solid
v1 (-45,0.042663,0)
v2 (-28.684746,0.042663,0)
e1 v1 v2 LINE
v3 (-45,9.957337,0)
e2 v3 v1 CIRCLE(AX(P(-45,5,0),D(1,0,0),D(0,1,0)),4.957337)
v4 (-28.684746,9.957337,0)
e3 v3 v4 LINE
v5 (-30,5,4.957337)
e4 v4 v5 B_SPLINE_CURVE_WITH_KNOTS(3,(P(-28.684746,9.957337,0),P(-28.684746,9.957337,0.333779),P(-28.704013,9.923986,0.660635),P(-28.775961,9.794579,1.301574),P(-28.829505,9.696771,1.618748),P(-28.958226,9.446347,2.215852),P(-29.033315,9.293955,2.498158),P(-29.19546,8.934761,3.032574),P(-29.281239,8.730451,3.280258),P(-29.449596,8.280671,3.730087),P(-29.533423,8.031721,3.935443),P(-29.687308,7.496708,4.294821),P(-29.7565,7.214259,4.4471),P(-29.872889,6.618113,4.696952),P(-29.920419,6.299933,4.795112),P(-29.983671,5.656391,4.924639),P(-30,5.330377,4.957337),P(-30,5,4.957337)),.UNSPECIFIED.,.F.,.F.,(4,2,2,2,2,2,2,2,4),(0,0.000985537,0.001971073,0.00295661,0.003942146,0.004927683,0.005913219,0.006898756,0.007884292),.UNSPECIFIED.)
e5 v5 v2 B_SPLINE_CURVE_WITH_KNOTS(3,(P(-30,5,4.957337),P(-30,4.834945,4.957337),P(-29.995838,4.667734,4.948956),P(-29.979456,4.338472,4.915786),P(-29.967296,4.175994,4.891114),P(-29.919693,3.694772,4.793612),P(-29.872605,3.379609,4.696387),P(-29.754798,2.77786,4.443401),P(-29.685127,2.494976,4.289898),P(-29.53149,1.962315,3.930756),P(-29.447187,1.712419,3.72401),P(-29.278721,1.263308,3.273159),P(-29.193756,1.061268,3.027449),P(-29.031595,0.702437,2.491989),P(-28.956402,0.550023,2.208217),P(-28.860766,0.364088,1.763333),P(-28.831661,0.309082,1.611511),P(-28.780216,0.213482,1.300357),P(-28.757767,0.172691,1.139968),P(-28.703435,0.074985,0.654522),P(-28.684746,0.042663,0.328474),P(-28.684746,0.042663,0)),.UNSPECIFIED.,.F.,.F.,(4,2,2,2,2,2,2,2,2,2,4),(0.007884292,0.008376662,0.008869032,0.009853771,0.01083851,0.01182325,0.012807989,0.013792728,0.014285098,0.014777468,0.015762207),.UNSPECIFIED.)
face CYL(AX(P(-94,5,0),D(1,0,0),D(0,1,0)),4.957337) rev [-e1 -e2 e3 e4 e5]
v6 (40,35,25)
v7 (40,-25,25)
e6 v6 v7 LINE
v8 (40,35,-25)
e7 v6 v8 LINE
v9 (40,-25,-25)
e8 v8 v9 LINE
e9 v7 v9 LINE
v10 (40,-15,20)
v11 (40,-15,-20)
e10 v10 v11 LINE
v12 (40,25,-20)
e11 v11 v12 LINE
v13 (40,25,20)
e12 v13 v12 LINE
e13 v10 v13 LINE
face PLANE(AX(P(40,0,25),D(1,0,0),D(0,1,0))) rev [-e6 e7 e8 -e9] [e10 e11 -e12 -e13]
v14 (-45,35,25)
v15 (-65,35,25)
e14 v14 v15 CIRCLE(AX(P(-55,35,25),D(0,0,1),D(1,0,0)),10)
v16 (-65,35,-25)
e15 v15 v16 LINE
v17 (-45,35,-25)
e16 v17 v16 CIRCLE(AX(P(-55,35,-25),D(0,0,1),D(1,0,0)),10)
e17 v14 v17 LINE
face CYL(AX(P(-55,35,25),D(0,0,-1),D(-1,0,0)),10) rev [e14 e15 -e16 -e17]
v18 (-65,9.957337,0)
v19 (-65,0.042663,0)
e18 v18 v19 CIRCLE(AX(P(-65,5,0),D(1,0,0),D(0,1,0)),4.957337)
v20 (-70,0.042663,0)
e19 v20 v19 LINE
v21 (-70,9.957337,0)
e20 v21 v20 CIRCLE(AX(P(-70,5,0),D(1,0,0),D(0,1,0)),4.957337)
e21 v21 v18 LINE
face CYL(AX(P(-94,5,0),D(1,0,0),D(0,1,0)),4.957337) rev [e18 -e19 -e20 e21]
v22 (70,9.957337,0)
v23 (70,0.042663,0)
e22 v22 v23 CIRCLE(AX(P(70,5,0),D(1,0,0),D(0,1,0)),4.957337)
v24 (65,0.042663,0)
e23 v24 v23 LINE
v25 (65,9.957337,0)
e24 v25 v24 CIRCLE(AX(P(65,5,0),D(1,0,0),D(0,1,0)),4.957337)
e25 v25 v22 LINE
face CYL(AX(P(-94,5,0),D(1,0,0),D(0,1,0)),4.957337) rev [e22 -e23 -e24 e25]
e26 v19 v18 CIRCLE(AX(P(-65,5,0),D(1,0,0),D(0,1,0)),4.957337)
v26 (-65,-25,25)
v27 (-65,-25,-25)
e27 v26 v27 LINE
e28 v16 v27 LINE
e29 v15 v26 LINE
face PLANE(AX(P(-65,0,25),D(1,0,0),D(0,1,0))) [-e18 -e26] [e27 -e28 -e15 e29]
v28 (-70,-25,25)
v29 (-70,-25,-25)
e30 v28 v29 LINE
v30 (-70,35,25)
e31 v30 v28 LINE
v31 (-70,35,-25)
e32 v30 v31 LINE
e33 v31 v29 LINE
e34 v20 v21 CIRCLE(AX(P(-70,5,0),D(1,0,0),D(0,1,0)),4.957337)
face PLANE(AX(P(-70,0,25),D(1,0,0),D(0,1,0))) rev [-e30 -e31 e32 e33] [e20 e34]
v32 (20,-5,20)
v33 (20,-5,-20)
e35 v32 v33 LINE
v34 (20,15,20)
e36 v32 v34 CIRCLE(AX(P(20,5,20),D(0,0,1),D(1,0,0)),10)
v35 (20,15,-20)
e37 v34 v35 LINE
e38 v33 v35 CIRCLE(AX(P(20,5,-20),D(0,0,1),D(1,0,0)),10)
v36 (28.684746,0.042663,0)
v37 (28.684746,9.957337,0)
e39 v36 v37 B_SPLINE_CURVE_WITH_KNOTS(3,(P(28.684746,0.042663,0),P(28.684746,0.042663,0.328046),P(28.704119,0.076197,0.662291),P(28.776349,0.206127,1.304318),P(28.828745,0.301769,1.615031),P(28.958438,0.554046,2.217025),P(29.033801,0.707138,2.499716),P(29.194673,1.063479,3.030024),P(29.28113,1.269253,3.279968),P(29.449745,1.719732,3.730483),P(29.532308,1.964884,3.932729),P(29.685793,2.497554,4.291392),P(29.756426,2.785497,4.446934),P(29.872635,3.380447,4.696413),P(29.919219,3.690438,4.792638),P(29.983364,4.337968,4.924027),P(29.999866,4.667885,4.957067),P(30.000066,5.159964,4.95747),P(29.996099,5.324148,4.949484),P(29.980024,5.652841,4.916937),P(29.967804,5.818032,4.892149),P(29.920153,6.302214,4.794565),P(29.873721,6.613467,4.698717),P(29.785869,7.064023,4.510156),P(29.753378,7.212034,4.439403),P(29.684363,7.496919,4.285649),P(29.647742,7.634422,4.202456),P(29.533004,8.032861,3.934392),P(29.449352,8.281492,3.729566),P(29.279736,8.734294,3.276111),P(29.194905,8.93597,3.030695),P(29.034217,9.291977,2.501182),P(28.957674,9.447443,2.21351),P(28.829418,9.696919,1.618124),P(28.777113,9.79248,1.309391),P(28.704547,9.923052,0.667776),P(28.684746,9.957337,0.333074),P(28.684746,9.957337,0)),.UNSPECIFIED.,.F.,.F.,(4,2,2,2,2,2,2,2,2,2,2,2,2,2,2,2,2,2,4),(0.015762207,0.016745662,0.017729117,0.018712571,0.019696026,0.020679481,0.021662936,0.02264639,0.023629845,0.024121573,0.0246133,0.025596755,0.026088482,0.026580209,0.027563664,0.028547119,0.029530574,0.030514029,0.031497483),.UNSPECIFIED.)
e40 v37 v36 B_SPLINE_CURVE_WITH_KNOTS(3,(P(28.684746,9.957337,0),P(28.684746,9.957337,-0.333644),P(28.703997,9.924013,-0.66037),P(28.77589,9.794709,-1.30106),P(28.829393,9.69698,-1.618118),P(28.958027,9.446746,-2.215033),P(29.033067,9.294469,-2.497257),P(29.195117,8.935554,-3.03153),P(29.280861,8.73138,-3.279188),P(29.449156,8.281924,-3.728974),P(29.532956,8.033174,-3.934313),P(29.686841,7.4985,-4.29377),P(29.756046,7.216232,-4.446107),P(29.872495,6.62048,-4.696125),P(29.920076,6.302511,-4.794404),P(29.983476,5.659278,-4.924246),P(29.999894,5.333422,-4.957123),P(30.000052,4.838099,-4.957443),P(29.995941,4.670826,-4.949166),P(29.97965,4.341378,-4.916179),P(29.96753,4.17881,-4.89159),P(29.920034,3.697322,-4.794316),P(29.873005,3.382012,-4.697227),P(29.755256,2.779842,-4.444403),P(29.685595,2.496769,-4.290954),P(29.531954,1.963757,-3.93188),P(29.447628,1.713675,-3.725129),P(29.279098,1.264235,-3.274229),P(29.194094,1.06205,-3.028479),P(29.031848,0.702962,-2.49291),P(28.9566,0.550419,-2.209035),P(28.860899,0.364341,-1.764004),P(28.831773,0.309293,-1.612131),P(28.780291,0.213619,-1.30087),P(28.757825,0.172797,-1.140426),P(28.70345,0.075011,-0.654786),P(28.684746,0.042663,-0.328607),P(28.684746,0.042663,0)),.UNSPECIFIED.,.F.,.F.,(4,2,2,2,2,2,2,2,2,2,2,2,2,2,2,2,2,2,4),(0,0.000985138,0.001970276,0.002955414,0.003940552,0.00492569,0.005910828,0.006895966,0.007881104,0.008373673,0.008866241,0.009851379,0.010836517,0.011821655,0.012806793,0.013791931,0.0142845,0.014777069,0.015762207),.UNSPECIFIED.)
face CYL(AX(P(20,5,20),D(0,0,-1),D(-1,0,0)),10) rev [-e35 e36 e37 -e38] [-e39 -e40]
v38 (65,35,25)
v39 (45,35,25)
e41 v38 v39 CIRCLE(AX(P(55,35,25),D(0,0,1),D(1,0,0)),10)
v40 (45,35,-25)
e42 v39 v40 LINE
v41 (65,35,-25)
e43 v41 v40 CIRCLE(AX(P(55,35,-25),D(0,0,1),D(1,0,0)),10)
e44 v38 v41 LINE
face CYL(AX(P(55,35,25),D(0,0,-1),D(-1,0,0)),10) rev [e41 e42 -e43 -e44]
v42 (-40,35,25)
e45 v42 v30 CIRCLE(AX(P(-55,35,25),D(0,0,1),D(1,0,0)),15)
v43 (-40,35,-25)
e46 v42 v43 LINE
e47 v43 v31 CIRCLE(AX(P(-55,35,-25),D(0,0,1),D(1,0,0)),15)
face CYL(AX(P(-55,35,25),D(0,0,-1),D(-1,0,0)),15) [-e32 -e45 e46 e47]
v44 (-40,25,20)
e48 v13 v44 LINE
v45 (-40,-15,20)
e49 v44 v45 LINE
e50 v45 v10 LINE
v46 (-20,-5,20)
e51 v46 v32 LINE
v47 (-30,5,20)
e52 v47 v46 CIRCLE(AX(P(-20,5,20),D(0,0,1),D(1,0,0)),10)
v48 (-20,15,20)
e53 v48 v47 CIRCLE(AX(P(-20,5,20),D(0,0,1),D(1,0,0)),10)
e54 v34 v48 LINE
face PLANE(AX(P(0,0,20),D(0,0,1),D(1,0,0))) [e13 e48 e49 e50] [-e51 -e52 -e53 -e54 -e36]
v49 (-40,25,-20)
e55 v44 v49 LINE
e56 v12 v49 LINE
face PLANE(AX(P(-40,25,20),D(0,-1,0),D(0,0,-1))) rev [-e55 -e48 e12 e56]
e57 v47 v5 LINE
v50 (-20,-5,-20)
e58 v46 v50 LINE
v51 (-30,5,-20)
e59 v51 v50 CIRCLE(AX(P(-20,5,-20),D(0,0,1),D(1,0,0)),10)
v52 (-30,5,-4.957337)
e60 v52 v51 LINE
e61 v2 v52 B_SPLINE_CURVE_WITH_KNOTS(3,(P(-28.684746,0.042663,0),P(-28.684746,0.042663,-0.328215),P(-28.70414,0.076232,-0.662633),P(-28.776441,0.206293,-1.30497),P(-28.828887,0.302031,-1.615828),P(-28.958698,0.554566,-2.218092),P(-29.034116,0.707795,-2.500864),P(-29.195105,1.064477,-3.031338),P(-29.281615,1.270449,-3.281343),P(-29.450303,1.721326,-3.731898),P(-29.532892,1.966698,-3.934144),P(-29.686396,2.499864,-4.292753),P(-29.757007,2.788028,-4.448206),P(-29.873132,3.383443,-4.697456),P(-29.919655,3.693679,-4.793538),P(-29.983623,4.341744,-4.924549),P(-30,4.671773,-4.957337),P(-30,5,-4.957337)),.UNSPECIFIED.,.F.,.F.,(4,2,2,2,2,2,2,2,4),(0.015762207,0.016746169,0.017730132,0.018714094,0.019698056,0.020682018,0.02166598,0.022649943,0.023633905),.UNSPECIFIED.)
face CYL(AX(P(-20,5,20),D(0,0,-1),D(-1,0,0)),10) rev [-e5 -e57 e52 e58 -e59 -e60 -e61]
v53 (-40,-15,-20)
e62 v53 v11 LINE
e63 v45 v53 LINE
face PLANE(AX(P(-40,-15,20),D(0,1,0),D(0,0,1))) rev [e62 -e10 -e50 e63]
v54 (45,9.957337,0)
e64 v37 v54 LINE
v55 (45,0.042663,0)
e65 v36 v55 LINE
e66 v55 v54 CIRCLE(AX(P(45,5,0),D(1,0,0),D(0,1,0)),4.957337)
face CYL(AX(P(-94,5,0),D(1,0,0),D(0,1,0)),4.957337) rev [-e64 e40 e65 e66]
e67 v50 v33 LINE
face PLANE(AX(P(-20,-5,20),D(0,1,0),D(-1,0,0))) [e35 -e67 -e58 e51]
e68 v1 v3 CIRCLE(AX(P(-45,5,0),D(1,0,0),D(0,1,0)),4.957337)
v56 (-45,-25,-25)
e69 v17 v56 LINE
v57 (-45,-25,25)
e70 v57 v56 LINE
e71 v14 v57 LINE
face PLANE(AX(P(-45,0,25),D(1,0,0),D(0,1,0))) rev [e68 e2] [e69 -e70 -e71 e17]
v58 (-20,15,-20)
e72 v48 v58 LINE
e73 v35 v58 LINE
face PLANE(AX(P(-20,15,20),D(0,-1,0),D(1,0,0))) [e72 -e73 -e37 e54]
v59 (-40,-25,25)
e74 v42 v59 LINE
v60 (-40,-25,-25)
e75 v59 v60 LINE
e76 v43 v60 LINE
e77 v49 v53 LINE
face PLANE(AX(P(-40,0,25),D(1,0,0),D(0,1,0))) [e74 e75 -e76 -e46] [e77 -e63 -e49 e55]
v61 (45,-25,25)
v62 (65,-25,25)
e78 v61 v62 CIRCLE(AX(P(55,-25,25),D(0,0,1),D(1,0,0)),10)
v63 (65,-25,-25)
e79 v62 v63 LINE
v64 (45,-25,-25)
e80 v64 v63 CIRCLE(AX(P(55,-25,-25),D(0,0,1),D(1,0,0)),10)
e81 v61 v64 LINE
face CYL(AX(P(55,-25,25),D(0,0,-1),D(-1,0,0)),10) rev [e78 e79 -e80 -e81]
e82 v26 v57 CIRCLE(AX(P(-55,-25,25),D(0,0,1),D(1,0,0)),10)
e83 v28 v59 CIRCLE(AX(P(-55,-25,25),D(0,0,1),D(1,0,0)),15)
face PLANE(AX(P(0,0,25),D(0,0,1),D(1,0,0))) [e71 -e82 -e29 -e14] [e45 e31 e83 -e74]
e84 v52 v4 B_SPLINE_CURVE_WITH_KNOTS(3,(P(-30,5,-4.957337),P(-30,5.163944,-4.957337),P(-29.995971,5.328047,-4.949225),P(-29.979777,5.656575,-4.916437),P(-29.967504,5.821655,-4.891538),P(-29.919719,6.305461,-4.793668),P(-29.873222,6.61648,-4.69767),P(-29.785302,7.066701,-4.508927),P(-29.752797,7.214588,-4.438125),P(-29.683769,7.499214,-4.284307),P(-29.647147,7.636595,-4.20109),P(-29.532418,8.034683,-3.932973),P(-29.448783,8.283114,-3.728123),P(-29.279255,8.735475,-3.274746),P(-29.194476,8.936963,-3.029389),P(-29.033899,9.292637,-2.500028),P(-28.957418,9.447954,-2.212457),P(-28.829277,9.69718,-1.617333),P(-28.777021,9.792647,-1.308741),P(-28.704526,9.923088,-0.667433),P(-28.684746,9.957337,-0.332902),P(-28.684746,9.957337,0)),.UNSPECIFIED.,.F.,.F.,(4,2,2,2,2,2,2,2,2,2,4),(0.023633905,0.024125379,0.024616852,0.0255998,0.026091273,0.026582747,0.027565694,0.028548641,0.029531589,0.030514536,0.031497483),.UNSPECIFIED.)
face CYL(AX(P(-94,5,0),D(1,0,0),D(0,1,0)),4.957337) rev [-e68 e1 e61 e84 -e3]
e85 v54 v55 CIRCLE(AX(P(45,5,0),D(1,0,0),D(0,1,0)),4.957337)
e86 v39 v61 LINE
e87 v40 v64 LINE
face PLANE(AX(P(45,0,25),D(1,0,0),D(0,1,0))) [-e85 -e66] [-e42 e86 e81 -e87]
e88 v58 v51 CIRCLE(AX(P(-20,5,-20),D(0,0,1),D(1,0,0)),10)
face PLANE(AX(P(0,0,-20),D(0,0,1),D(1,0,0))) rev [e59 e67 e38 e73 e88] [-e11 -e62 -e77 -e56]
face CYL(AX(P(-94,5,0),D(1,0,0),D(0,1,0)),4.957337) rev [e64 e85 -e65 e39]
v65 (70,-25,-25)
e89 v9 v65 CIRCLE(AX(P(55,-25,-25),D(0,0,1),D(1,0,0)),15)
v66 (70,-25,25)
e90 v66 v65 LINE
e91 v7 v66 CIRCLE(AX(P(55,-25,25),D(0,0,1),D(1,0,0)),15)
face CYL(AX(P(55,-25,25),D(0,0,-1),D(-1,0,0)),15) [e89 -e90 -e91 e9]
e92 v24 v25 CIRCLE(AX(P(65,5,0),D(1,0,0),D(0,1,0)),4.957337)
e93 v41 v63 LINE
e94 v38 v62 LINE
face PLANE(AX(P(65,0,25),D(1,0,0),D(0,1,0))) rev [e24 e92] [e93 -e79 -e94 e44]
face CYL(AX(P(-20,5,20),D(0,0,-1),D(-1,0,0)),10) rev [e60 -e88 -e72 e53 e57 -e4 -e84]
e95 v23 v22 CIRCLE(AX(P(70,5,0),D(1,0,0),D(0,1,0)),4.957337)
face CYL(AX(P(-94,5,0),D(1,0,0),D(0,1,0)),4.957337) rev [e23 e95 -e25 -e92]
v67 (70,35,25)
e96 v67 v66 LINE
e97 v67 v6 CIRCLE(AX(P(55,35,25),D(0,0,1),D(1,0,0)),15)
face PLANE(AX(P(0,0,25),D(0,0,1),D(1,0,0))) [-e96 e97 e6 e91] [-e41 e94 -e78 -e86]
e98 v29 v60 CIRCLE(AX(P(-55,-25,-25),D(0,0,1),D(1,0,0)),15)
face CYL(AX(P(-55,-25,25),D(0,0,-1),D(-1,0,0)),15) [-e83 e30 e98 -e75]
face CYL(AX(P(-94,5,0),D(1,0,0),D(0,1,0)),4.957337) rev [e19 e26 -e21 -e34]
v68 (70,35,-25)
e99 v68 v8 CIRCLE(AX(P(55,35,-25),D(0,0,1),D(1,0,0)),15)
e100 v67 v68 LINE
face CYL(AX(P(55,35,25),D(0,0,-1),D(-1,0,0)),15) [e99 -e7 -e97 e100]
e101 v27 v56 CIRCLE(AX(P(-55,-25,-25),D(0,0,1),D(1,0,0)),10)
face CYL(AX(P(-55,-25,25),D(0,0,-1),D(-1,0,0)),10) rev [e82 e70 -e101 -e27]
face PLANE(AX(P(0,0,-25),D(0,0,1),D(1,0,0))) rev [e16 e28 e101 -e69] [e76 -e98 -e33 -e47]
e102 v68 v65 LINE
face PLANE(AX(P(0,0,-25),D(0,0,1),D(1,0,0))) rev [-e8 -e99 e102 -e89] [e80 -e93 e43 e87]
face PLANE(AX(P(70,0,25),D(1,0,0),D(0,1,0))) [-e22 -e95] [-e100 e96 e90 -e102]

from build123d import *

# Parameters (mm, degrees)
END_LOOPS_DEPTH       = 25
END_LOOPS_2_DEPTH     = 25
CENTRE_BLOCK_SKETCH_W = 80
CENTRE_BLOCK_SKETCH_H = 40
CENTRE_BLOCK_DEPTH    = 20
CROSS_HOLE_SKETCH_R   = 4.957337167
CROSS_HOLE_DEPTH      = 164


with BuildPart() as part:
    # End Loops Sketch → End Loops (new, symmetric)
    with BuildSketch(Plane.XY):
        with BuildLine():
            Line((-40, 35), (-40, -25))
            ThreePointArc((-40, -25), (-55, -40), (-70, -25))
            Line((-70, -25), (-70, 35))
            ThreePointArc((-70, 35), (-55, 50), (-40, 35))
        make_face()
        with BuildLine():
            Line((-45, 35), (-45, -25))
            ThreePointArc((-45, -25), (-55, -35), (-65, -25))
            Line((-65, -25), (-65, 35))
            ThreePointArc((-65, 35), (-55, 45), (-45, 35))
        make_face(mode=Mode.SUBTRACT)
    extrude(amount=END_LOOPS_DEPTH, both=True)



with BuildPart() as body_2:
    # End Loops Sketch → End Loops 2 (new, symmetric)
    with BuildSketch(Plane.XY):
        with BuildLine():
            Line((70, 35), (70, -25))
            ThreePointArc((70, -25), (55, -40), (40, -25))
            Line((40, -25), (40, 35))
            ThreePointArc((40, 35), (55, 50), (70, 35))
        make_face()
        with BuildLine():
            Line((65, 35), (65, -25))
            ThreePointArc((65, -25), (55, -35), (45, -25))
            Line((45, -25), (45, 35))
            ThreePointArc((45, 35), (55, 45), (65, 35))
        make_face(mode=Mode.SUBTRACT)
    extrude(amount=END_LOOPS_2_DEPTH, both=True)


with BuildPart() as part_1:
    add(part.part)

    add(body_2.part)  # Centre Block merges body 2
    # Centre Block Sketch → Centre Block (add, symmetric)
    with BuildSketch(Plane.XY):
        with Locations((0, 5)):
            Rectangle(CENTRE_BLOCK_SKETCH_W, CENTRE_BLOCK_SKETCH_H)
        with BuildLine():
            Line((-20, 15), (20, 15))
            ThreePointArc((20, 15), (30, 5), (20, -5))
            Line((20, -5), (-20, -5))
            ThreePointArc((-20, -5), (-30, 5), (-20, 15))
        make_face(mode=Mode.SUBTRACT)
    extrude(amount=CENTRE_BLOCK_DEPTH, both=True)

    # Cross Hole Sketch → Cross Hole (cut)
    with BuildSketch(Plane(origin=(70, 0, 0), x_dir=(0, 0, -1), z_dir=(1, 0, 0))):
        with Locations(Location((0, 5, 0), (0, 0, 90))):
            Circle(CROSS_HOLE_SKETCH_R)
    extrude(amount=-CROSS_HOLE_DEPTH, mode=Mode.SUBTRACT)


solid = part_1.part
